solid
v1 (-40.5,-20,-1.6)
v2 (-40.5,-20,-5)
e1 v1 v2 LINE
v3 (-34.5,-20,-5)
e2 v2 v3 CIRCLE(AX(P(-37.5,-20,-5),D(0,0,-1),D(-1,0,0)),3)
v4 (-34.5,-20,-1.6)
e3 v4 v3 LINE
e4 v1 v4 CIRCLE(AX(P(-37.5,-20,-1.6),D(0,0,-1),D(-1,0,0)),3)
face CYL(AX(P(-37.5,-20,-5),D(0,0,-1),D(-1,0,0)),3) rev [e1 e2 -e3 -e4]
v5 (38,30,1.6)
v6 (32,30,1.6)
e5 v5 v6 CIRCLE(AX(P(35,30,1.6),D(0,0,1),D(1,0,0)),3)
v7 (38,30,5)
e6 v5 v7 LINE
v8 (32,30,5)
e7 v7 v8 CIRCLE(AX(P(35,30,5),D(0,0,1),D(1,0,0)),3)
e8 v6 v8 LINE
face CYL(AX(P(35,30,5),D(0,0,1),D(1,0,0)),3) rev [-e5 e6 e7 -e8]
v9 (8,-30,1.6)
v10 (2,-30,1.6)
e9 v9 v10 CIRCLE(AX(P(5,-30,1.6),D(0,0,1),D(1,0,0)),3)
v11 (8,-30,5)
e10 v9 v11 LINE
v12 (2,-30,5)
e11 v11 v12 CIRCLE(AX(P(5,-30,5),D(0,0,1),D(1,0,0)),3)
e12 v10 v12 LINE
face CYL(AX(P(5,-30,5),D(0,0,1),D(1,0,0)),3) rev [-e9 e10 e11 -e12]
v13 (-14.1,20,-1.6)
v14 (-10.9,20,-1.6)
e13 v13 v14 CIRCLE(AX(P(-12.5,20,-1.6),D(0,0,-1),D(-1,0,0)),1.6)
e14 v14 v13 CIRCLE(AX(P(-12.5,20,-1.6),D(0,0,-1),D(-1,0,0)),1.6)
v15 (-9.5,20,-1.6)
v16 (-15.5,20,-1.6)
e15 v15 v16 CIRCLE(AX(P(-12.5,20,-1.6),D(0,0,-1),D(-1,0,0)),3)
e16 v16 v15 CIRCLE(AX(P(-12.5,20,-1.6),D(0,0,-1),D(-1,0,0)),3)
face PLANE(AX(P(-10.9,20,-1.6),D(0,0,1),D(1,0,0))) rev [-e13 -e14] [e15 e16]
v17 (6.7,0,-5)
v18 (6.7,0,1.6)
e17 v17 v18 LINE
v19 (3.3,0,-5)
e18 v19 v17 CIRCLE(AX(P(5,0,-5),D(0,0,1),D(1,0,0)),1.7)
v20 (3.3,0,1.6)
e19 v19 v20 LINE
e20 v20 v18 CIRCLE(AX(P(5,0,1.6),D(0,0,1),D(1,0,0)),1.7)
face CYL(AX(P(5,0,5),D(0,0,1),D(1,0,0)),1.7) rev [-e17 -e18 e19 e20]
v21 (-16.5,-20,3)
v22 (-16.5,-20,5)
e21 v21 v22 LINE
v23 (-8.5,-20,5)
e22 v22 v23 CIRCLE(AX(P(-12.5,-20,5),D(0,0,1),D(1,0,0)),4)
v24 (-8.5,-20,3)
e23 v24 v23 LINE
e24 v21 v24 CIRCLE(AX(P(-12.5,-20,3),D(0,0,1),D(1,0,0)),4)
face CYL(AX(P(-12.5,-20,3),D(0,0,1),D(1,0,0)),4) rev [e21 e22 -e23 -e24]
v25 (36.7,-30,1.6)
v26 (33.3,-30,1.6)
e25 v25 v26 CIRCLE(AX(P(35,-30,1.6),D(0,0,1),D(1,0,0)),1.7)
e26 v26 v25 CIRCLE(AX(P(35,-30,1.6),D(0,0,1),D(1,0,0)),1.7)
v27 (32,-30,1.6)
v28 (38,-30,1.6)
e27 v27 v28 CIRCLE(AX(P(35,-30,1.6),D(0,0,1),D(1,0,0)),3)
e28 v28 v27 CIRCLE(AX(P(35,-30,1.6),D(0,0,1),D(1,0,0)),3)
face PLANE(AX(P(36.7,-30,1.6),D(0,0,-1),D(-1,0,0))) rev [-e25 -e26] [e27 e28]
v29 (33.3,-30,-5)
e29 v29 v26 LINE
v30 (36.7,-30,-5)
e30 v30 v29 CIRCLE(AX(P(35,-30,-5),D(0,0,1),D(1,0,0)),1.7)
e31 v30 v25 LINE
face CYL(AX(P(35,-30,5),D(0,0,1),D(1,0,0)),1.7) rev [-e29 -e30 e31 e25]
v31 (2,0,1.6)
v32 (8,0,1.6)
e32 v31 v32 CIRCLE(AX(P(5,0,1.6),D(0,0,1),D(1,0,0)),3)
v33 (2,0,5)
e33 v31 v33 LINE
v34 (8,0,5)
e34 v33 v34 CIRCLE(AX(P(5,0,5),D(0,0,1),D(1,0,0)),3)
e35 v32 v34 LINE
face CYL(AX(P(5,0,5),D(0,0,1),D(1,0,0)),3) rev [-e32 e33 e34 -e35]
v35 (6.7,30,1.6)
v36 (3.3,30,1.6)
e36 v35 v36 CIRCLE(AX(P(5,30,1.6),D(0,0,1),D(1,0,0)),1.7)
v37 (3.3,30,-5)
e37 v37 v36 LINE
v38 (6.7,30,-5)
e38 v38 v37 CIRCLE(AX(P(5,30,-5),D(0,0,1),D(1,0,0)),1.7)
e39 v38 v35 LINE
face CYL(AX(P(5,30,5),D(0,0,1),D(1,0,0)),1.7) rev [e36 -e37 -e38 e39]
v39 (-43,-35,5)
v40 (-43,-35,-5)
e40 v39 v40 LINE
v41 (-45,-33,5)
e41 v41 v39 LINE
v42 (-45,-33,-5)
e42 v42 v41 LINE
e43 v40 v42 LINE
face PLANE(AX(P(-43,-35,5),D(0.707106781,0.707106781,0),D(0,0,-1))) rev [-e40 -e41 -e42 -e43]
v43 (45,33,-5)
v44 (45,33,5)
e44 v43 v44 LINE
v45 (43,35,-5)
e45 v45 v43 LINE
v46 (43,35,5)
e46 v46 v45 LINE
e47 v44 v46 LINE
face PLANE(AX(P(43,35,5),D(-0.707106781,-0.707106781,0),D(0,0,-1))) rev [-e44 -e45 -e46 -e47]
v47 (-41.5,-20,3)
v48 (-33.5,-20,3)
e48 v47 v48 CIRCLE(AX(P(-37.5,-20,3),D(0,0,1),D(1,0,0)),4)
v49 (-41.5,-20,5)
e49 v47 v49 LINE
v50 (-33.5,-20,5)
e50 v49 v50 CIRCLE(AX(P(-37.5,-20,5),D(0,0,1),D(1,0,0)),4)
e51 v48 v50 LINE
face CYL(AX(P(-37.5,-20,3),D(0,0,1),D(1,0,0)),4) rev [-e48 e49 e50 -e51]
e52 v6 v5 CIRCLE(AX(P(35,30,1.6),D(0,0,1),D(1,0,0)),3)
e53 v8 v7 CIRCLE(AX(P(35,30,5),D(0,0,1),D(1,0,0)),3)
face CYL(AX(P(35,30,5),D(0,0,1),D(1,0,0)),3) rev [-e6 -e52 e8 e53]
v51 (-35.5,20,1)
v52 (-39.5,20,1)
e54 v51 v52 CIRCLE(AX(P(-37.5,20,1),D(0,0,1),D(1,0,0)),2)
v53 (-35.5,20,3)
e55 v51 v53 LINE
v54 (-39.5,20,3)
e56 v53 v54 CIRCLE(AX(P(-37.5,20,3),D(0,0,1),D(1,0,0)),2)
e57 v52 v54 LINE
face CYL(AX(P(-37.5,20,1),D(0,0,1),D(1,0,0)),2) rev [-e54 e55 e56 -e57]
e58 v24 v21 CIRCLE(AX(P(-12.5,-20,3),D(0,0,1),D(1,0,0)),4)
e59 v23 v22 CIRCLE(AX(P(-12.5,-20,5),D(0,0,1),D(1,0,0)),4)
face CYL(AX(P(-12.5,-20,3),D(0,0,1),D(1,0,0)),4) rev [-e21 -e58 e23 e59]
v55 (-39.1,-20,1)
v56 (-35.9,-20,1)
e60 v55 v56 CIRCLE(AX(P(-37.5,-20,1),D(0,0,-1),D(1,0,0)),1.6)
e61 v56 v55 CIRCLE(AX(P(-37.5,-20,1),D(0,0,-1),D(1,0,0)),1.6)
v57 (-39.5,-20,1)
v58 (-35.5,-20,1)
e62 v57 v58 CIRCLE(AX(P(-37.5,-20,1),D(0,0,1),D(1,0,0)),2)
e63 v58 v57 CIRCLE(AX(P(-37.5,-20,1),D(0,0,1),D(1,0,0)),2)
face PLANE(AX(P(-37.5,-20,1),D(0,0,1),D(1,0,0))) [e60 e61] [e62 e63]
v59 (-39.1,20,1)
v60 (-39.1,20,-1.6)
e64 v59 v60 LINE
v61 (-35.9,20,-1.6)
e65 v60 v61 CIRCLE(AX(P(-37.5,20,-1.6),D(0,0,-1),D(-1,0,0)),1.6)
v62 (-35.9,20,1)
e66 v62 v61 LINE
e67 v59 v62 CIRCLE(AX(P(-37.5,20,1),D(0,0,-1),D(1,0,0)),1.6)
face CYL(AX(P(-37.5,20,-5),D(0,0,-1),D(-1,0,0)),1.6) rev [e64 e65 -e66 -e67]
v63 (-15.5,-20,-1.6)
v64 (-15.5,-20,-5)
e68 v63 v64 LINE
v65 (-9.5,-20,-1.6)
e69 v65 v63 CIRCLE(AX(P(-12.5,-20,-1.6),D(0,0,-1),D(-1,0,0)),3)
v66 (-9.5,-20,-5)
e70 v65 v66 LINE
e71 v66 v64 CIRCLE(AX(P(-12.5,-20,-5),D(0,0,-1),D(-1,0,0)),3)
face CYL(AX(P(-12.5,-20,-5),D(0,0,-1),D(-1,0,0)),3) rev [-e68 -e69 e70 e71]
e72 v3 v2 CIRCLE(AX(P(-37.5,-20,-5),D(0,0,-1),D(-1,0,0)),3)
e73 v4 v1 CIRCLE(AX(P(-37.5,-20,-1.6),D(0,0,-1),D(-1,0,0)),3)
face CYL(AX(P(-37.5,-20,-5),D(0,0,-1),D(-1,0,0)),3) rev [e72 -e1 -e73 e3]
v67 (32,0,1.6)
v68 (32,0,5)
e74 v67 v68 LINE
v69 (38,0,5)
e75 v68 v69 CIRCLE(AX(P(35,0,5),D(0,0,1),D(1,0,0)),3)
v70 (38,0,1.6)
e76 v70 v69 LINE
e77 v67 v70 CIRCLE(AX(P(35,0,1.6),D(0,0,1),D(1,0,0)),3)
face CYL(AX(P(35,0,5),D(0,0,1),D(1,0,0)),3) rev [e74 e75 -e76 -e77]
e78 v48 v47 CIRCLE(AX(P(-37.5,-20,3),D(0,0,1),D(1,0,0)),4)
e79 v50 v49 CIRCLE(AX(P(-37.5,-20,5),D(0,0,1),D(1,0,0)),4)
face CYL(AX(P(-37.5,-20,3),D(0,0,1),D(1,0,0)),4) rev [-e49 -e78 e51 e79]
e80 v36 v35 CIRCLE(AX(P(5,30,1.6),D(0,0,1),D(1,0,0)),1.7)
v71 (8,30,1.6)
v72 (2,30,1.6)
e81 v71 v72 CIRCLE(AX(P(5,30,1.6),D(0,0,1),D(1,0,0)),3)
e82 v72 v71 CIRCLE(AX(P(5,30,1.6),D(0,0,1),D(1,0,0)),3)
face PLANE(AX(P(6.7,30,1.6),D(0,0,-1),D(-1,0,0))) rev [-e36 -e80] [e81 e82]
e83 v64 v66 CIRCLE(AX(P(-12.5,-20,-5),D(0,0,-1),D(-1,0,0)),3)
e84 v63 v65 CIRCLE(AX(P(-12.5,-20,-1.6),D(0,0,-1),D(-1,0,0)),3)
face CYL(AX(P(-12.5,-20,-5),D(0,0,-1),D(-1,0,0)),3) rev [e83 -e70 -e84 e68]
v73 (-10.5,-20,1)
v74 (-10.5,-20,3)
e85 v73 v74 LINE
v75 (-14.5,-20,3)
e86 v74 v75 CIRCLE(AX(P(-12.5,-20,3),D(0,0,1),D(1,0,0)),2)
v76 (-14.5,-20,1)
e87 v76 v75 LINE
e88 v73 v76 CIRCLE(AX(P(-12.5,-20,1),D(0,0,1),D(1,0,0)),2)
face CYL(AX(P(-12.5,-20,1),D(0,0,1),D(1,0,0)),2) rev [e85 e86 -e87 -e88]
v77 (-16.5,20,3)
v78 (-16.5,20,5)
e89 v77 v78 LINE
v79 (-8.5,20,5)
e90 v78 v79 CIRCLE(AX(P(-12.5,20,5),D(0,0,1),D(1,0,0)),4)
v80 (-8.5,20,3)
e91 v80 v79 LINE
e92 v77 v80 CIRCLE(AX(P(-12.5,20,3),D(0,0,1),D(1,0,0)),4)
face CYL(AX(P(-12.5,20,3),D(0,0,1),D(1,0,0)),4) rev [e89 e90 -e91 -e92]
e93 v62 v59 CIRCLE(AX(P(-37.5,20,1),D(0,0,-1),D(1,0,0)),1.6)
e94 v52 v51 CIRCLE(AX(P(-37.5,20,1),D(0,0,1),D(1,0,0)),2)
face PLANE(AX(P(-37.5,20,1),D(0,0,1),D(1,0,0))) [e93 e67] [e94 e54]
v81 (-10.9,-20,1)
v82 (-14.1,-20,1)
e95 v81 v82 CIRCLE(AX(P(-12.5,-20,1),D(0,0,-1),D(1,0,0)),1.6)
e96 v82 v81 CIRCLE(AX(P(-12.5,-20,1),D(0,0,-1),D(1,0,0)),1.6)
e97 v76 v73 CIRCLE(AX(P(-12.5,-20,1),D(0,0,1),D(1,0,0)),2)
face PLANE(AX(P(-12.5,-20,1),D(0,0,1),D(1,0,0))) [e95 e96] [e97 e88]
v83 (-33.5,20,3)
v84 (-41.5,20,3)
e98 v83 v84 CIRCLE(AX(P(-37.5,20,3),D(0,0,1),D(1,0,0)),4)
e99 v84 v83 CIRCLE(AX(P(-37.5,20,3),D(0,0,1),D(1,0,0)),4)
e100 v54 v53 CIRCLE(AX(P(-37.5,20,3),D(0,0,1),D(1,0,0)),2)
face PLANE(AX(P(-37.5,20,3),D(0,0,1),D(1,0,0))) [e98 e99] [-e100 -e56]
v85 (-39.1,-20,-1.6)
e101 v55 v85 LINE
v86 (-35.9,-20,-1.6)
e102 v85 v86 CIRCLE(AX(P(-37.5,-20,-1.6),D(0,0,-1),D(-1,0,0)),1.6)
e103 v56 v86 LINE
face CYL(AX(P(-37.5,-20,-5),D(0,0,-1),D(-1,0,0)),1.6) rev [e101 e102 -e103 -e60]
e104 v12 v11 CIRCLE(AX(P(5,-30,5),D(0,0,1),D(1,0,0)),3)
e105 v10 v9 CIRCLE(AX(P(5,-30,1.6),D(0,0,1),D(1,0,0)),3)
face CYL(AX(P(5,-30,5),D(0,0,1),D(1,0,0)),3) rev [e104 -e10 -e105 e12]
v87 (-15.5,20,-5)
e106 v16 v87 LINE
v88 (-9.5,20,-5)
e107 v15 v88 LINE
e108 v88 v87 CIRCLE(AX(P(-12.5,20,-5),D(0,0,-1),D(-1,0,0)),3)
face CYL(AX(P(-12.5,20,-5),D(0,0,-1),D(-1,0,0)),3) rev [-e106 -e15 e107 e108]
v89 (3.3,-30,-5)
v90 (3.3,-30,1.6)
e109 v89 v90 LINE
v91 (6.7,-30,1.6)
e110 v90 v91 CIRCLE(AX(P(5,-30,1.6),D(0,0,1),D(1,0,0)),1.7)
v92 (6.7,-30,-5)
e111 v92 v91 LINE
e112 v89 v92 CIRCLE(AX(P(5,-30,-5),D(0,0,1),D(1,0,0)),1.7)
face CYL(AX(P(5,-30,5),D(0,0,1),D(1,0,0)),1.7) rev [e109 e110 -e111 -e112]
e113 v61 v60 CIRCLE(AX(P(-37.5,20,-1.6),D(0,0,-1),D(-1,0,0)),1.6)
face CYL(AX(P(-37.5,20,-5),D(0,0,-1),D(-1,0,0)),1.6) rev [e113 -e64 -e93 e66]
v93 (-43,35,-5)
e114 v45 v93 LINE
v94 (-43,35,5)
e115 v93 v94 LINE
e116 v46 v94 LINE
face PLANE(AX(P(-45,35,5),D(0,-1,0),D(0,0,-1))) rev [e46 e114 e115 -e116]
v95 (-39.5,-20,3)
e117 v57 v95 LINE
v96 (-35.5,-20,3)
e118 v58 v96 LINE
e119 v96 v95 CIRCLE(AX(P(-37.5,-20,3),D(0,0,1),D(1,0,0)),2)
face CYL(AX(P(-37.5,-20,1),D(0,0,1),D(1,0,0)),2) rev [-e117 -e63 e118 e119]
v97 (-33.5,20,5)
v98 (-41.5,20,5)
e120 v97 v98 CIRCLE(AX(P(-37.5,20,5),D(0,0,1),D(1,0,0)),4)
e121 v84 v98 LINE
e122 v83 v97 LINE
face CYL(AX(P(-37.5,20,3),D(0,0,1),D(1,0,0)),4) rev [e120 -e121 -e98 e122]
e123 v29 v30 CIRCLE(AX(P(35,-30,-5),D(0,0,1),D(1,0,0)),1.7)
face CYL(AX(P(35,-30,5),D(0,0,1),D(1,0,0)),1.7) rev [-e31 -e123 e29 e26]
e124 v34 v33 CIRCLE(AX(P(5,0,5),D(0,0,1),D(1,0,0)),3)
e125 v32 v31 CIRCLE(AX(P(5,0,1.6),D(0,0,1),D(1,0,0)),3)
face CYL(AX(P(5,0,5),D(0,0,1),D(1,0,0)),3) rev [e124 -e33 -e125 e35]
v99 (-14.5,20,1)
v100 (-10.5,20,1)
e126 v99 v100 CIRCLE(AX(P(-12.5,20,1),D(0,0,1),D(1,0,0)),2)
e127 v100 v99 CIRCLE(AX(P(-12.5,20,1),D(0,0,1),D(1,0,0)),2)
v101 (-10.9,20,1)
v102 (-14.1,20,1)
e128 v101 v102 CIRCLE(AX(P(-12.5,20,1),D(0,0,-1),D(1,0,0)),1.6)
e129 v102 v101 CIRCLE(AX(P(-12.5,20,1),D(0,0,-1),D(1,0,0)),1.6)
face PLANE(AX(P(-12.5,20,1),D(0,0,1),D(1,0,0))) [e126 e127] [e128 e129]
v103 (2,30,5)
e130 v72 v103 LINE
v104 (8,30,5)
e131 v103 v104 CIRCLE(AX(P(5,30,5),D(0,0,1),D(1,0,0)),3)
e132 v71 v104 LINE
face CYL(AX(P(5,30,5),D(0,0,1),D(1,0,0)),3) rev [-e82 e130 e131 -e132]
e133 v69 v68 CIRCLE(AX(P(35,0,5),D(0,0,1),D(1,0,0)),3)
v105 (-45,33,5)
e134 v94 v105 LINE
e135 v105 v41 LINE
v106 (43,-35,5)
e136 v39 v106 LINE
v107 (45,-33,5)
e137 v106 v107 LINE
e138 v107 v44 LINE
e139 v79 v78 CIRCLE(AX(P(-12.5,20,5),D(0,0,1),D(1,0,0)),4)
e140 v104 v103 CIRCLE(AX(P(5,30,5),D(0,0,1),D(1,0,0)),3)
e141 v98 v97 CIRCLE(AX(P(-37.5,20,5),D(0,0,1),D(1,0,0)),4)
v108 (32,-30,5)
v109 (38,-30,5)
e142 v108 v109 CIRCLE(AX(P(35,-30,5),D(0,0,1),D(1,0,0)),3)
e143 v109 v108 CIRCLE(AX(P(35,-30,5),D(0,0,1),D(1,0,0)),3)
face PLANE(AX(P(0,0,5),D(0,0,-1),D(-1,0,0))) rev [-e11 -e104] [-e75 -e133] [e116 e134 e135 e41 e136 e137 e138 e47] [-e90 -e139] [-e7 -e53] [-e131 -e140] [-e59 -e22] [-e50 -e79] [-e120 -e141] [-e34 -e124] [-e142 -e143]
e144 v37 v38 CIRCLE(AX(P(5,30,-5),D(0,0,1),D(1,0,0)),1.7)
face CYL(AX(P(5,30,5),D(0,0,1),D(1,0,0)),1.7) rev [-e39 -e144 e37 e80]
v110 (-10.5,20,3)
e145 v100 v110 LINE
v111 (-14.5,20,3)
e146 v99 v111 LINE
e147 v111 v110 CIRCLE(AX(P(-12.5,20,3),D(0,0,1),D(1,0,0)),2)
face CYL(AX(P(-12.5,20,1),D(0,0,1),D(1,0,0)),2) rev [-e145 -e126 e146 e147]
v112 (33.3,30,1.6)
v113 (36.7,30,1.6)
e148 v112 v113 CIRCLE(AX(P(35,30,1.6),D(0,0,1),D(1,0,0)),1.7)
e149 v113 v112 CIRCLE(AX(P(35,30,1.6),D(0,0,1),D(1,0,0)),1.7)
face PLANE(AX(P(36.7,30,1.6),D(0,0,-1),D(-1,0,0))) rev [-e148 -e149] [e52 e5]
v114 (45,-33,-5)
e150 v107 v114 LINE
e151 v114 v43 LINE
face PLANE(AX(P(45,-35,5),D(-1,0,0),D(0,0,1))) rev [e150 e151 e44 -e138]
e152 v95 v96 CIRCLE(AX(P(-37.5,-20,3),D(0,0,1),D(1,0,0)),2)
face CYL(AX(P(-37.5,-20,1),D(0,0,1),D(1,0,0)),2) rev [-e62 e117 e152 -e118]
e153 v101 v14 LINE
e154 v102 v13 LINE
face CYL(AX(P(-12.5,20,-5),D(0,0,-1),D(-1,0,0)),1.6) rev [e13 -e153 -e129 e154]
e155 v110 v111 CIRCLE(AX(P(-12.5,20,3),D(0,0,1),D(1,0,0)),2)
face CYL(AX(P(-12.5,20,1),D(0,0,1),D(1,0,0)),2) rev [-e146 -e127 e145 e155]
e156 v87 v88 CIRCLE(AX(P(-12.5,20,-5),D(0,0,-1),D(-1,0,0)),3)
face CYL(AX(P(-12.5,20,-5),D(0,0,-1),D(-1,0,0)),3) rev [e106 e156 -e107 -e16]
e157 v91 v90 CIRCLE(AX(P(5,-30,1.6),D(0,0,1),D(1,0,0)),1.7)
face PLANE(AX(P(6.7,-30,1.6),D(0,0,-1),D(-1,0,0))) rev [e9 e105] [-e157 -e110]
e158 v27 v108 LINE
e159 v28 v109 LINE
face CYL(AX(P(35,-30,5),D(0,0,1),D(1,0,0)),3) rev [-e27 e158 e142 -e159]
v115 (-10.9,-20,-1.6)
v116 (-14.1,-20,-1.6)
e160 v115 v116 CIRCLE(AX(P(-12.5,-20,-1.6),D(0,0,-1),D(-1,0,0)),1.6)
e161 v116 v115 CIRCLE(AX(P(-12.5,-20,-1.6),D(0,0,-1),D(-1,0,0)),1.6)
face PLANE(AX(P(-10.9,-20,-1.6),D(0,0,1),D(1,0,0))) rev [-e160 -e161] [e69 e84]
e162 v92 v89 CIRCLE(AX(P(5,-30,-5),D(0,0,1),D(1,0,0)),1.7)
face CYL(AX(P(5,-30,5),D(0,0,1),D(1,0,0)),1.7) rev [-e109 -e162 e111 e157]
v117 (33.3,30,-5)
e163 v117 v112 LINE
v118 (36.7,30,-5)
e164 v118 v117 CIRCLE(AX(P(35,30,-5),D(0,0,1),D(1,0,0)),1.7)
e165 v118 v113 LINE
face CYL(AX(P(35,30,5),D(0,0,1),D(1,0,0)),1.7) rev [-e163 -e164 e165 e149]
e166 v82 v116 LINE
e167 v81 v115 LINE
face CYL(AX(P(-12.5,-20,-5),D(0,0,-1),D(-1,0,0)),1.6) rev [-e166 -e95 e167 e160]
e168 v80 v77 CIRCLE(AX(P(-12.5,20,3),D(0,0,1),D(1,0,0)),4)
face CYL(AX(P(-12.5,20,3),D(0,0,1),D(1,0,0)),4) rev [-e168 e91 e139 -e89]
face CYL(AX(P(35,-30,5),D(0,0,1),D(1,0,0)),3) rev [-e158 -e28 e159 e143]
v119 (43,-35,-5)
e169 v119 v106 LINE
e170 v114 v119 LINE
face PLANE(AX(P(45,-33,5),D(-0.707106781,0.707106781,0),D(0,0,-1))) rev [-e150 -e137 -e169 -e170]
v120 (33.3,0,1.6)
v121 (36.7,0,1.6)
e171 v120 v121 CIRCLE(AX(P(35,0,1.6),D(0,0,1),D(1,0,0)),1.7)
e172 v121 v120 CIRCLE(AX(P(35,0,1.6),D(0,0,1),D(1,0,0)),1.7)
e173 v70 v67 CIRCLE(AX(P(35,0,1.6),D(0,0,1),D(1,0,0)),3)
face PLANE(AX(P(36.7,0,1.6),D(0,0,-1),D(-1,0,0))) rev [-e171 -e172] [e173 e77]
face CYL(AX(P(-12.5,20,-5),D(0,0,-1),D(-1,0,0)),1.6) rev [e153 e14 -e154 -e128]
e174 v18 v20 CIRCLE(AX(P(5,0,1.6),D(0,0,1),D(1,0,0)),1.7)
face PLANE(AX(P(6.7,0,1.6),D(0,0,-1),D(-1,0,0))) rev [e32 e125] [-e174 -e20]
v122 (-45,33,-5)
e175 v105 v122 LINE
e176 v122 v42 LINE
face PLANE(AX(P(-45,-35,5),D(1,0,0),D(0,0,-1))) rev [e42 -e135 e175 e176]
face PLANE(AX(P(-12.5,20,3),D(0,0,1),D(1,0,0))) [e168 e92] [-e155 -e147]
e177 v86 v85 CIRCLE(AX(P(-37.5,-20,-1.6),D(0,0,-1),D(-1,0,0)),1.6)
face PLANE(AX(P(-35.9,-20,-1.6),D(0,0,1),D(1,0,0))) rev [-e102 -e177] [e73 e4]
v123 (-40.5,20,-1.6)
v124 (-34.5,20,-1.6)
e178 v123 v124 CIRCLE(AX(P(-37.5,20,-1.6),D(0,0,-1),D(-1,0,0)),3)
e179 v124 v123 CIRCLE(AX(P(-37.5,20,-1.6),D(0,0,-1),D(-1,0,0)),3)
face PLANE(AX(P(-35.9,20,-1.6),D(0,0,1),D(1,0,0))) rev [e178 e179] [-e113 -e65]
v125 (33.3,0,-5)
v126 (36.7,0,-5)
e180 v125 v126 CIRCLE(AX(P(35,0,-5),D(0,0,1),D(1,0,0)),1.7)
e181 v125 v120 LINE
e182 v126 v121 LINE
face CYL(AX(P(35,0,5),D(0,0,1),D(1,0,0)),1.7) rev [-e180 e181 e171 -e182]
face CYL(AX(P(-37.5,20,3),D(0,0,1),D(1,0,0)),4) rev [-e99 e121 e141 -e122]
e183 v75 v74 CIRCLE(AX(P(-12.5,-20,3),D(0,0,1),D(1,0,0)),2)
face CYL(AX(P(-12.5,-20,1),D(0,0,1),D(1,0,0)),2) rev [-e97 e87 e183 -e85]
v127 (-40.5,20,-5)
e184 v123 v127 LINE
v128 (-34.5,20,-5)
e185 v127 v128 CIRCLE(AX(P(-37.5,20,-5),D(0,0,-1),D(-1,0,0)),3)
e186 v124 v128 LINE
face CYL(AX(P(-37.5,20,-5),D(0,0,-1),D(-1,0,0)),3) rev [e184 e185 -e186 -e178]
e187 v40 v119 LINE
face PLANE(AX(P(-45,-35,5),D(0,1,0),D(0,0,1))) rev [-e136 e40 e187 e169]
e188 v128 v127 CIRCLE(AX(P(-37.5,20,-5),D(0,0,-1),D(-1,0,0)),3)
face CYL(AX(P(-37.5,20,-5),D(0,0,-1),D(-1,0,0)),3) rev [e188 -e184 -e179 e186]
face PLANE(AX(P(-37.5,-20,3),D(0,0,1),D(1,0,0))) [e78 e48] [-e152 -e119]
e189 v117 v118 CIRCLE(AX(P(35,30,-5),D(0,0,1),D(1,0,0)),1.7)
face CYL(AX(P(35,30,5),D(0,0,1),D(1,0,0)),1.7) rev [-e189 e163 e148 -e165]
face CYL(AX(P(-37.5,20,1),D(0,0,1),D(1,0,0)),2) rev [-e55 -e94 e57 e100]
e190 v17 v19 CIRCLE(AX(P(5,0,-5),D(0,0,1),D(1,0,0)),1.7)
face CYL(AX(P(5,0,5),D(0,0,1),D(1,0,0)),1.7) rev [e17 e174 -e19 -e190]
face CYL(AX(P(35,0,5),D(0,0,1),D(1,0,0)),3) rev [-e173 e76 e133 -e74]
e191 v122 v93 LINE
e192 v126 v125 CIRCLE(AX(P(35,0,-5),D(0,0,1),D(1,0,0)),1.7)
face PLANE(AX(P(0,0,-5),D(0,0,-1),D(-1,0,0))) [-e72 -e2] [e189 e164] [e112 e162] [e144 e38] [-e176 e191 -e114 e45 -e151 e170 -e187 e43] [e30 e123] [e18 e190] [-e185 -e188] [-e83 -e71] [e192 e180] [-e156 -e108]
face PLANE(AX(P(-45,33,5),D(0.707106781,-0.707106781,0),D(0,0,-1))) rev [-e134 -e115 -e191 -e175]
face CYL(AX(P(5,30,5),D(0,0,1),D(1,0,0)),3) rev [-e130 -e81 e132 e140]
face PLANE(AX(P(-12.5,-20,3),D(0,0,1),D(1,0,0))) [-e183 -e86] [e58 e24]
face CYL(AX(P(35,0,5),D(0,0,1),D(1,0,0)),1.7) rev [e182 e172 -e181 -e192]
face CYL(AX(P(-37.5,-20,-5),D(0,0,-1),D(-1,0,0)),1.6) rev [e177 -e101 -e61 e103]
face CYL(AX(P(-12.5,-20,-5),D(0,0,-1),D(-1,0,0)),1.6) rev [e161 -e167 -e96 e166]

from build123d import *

# Parameters (mm, degrees)
SKETCH_1_W                = 90
SKETCH_1_H                = 70
EXTRUDE_1_DEPTH           = 5
HOLE_WIZARD_1_D           = 3.4
HOLE_WIZARD_1_CBORE_D     = 6
HOLE_WIZARD_1_CBORE_DEPTH = 3.4
HOLE_WIZARD_3_D           = 3.2
HOLE_WIZARD_3_CBORE_D     = 6
HOLE_WIZARD_3_CBORE_DEPTH = 3.4
SKETCH_6_R                = 4
CUT_EXTRUDE_1_DEPTH       = 2
SKETCH_8_R                = 2
CUT_EXTRUDE_2_DEPTH       = 2
CHAMFER_1_SIZE            = 2


with BuildPart() as part:
    # 草图1 → 凸台-拉伸1 (new, symmetric)
    with BuildSketch(Plane.XY):
        Rectangle(SKETCH_1_W, SKETCH_1_H)
    extrude(amount=EXTRUDE_1_DEPTH, both=True)

    # 打孔尺寸(%根据)内六角圆柱头螺钉的类型1 (through all)
    with Locations(Plane.XY.offset(5)):
        with Locations((5, 30), (5, 0), (5, -30), (35, 30), (35, 0), (35, -30)):
            CounterBoreHole(HOLE_WIZARD_1_D / 2, HOLE_WIZARD_1_CBORE_D / 2, HOLE_WIZARD_1_CBORE_DEPTH)

    # 打孔尺寸(%根据)内六角圆柱头螺钉的类型3 (through all)
    with Locations(Plane(origin=(0, 0, -5), x_dir=(-1, 0, 0), z_dir=(0, 0, -1))):
        with Locations((37.5, 20), (12.5, 20), (12.5, -20), (37.5, -20)):
            CounterBoreHole(HOLE_WIZARD_3_D / 2, HOLE_WIZARD_3_CBORE_D / 2, HOLE_WIZARD_3_CBORE_DEPTH)

    # 草图6 → 切除-拉伸1 (cut)
    with BuildSketch(Plane.XY.offset(5)):
        with Locations((-37.5, 20)):
            Circle(SKETCH_6_R)
        with Locations((-12.5, 20)):
            Circle(SKETCH_6_R)
        with Locations((-37.5, -20)):
            Circle(SKETCH_6_R)
        with Locations((-12.5, -20)):
            Circle(SKETCH_6_R)
    extrude(amount=-CUT_EXTRUDE_1_DEPTH, mode=Mode.SUBTRACT)

    # 草图8 → 切除-拉伸2 (cut)
    with BuildSketch(Plane.XY.offset(3)):
        with Locations((-37.5, 20)):
            Circle(SKETCH_8_R)
        with Locations((-37.5, -20)):
            Circle(SKETCH_8_R)
        with Locations((-12.5, -20)):
            Circle(SKETCH_8_R)
        with Locations((-12.5, 20)):
            Circle(SKETCH_8_R)
    extrude(amount=-CUT_EXTRUDE_2_DEPTH, mode=Mode.SUBTRACT)

    # 倒角1
    chamfer_1_edges = [part.edges().sort_by_distance(p)[0] for p in [
        (45, -35, 0),
        (-45, -35, 0),
        (-45, 35, 0),
        (45, 35, 0),
    ]]
    chamfer(chamfer_1_edges, length=CHAMFER_1_SIZE)


solid = part.part
